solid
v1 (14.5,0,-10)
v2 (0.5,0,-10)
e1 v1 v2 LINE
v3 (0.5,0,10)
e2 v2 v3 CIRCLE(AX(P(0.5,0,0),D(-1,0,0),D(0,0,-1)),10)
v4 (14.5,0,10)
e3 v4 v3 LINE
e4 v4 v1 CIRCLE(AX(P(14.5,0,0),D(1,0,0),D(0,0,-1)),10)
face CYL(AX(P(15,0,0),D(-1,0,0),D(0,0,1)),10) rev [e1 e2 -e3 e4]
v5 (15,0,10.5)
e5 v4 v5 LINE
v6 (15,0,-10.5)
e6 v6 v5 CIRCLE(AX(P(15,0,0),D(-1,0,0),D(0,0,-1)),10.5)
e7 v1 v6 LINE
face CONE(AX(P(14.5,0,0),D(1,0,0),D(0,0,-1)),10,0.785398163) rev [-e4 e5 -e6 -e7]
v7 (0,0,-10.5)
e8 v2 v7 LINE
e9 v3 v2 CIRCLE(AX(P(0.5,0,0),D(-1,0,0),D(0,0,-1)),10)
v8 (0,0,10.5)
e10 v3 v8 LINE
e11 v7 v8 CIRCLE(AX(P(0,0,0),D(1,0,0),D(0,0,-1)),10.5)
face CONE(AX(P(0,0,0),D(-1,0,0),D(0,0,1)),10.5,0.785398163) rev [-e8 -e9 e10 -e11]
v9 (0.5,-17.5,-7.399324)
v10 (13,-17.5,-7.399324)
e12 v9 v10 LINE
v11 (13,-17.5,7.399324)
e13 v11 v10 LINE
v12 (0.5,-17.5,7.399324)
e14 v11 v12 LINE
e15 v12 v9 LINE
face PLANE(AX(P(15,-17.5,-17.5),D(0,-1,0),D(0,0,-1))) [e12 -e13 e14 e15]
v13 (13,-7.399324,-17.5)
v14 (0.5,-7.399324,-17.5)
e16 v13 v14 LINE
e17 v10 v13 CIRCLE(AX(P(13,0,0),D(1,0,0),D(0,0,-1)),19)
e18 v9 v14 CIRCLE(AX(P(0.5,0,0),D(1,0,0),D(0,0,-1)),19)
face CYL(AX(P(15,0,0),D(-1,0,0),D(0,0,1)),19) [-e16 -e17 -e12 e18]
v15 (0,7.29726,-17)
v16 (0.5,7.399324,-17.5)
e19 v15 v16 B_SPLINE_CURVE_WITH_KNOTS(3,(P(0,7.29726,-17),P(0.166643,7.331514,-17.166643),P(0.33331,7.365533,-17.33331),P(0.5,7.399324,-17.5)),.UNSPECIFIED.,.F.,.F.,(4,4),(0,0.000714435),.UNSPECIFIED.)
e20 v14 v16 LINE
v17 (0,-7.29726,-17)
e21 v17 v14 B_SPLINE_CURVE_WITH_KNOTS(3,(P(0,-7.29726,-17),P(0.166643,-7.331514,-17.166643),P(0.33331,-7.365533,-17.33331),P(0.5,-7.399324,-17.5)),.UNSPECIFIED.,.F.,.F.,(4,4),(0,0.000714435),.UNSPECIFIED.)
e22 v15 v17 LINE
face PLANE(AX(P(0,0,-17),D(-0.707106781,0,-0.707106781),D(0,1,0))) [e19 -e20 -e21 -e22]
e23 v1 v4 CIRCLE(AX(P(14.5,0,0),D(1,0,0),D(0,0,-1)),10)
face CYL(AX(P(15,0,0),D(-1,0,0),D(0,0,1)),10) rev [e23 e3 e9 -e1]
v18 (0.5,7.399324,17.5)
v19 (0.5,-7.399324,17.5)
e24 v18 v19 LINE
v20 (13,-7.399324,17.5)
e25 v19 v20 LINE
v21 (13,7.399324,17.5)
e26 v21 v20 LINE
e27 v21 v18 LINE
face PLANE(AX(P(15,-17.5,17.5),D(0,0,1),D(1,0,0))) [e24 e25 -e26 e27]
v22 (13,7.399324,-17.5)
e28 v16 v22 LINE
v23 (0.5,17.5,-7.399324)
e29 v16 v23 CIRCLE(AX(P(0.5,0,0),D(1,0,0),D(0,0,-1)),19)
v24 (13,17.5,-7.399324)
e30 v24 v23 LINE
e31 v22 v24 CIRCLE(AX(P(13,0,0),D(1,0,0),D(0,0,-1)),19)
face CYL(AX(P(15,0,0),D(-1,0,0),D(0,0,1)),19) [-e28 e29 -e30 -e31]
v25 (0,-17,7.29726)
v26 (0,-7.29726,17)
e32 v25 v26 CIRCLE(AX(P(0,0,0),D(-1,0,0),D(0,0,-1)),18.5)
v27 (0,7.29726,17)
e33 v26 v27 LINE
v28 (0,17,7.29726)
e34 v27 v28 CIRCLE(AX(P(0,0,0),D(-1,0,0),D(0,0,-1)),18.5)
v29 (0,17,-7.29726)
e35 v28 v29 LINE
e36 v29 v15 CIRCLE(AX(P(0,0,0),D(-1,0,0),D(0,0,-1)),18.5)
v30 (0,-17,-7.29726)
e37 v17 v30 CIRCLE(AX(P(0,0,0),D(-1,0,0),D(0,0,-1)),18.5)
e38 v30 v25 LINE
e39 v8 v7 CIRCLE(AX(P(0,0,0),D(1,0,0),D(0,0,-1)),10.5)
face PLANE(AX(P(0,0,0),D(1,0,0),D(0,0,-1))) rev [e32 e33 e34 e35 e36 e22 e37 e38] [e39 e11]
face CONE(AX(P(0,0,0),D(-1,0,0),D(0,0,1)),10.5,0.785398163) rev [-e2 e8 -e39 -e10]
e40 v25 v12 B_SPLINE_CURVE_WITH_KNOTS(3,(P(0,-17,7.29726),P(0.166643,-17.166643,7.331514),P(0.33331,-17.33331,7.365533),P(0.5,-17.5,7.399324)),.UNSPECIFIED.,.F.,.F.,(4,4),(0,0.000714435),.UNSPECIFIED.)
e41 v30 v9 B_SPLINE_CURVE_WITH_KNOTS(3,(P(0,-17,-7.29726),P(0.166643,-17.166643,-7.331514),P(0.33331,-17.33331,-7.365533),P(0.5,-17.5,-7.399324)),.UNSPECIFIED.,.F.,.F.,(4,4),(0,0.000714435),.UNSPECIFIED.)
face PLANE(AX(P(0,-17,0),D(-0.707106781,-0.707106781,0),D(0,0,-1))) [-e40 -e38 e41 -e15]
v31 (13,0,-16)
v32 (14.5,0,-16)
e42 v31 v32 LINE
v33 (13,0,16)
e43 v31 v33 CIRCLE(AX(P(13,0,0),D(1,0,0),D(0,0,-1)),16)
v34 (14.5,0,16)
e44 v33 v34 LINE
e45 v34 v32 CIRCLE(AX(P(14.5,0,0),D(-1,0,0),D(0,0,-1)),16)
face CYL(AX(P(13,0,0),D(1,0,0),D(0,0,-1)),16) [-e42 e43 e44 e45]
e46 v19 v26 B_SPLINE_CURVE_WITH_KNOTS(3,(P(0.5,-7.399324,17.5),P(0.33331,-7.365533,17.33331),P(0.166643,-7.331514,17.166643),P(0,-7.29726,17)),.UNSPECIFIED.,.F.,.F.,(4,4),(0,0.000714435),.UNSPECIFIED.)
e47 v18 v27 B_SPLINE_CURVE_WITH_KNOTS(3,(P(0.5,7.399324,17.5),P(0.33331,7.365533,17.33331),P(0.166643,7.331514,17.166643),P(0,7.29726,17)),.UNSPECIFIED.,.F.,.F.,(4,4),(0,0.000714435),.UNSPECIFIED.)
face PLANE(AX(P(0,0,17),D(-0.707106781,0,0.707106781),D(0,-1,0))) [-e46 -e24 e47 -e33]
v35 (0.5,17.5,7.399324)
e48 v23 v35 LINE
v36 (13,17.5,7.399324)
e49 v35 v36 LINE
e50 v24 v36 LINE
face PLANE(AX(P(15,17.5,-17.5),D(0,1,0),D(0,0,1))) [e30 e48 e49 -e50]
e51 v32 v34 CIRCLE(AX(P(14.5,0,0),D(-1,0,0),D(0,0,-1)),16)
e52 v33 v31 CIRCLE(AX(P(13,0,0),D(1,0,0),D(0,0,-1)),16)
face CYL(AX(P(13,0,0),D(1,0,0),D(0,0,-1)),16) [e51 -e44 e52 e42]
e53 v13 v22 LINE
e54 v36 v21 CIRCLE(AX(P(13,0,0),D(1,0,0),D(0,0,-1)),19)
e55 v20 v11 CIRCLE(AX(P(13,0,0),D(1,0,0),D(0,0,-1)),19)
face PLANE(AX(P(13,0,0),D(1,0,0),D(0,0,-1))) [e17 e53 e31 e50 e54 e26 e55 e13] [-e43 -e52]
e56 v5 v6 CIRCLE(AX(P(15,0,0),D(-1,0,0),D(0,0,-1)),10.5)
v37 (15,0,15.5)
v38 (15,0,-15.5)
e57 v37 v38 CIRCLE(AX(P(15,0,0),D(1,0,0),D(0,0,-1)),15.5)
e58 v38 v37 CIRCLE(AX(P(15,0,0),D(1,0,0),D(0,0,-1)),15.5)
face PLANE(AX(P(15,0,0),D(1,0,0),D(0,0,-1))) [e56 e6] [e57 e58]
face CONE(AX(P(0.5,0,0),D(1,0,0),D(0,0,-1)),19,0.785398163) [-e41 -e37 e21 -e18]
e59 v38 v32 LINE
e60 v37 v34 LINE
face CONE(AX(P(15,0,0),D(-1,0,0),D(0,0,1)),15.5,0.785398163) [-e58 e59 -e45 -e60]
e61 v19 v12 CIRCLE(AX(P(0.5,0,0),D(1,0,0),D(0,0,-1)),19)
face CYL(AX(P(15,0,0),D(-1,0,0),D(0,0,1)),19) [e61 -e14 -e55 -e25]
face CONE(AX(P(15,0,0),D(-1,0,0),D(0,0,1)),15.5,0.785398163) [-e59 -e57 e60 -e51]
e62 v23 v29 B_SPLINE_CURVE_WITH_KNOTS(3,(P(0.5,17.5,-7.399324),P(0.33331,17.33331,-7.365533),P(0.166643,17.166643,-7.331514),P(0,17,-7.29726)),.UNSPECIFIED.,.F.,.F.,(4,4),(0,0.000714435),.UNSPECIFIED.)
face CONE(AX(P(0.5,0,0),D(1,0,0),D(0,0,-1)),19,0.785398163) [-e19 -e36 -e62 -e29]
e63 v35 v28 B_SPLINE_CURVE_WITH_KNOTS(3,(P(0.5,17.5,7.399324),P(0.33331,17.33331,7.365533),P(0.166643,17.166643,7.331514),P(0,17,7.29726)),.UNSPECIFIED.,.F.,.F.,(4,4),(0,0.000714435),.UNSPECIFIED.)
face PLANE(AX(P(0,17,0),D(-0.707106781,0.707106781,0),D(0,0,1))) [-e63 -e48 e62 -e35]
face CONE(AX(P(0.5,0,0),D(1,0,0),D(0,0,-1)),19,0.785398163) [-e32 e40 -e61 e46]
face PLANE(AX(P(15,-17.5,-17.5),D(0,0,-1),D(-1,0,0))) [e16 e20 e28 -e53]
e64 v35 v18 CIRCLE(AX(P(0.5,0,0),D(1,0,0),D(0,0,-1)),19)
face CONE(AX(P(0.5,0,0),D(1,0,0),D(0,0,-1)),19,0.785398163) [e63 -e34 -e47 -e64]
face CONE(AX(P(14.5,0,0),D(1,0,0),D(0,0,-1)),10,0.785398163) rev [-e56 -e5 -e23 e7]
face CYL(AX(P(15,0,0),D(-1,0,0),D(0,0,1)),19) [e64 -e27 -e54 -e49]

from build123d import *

# Parameters (mm, degrees)
SKETCH1_R           = 19
SKETCH1_R_2         = 10
BOSS_EXTRUDE1_DEPTH = 15
SKETCH2_OUTSIDE_W   = 51.158
SKETCH2_OUTSIDE_H   = 51.158
SKETCH2_OUTSIDE_R   = 16
CUT_EXTRUDE1_DEPTH  = 2
SKETCH3_OUTSIDE_W   = 51.158
SKETCH3_OUTSIDE_H   = 51.158
SKETCH3_OUTSIDE_W_2 = 35
SKETCH3_OUTSIDE_H_2 = 35
CUT_EXTRUDE2_DEPTH  = 31.773365107
CHAMFER1_SIZE       = 0.5


with BuildPart() as part:
    # Sketch1 → Boss-Extrude1 (new body)
    with BuildSketch(Plane(origin=(0, 0, 0), x_dir=(0, 0, -1), z_dir=(1, 0, 0))):
        Circle(SKETCH1_R)
        Circle(SKETCH1_R_2, mode=Mode.SUBTRACT)
    extrude(amount=BOSS_EXTRUDE1_DEPTH)

    # Sketch2 outside → Cut-Extrude1 (cut)
    with BuildSketch(Plane(origin=(15, 0, 0), x_dir=(0, 0, -1), z_dir=(1, 0, 0))):
        Rectangle(SKETCH2_OUTSIDE_W, SKETCH2_OUTSIDE_H)
        Circle(SKETCH2_OUTSIDE_R, mode=Mode.SUBTRACT)
    extrude(amount=-CUT_EXTRUDE1_DEPTH, mode=Mode.SUBTRACT)

    # Sketch3 outside → Cut-Extrude2 (cut, through all)
    with BuildSketch(Plane.ZY):
        Rectangle(SKETCH3_OUTSIDE_W, SKETCH3_OUTSIDE_H)
        Rectangle(SKETCH3_OUTSIDE_W_2, SKETCH3_OUTSIDE_H_2, mode=Mode.SUBTRACT)
    extrude(amount=-CUT_EXTRUDE2_DEPTH, mode=Mode.SUBTRACT)

    # Chamfer1
    chamfer1_edges = [part.edges().sort_by_distance(p)[0] for p in [
        (15, 0, 16),
        (0, 13.435028843, -13.435028843),
        (0, 13.435028843, 13.435028843),
        (0, -13.435028843, 13.435028843),
        (0, -13.435028843, -13.435028843),
        (0, 0, 17.5),
        (0, -17.5, 0),
        (0, 0, -17.5),
        (0, 17.5, 0),
        (0, 0, 10),
        (15, 0, 10),
    ]]
    chamfer(chamfer1_edges, length=CHAMFER1_SIZE)


solid = part.part
